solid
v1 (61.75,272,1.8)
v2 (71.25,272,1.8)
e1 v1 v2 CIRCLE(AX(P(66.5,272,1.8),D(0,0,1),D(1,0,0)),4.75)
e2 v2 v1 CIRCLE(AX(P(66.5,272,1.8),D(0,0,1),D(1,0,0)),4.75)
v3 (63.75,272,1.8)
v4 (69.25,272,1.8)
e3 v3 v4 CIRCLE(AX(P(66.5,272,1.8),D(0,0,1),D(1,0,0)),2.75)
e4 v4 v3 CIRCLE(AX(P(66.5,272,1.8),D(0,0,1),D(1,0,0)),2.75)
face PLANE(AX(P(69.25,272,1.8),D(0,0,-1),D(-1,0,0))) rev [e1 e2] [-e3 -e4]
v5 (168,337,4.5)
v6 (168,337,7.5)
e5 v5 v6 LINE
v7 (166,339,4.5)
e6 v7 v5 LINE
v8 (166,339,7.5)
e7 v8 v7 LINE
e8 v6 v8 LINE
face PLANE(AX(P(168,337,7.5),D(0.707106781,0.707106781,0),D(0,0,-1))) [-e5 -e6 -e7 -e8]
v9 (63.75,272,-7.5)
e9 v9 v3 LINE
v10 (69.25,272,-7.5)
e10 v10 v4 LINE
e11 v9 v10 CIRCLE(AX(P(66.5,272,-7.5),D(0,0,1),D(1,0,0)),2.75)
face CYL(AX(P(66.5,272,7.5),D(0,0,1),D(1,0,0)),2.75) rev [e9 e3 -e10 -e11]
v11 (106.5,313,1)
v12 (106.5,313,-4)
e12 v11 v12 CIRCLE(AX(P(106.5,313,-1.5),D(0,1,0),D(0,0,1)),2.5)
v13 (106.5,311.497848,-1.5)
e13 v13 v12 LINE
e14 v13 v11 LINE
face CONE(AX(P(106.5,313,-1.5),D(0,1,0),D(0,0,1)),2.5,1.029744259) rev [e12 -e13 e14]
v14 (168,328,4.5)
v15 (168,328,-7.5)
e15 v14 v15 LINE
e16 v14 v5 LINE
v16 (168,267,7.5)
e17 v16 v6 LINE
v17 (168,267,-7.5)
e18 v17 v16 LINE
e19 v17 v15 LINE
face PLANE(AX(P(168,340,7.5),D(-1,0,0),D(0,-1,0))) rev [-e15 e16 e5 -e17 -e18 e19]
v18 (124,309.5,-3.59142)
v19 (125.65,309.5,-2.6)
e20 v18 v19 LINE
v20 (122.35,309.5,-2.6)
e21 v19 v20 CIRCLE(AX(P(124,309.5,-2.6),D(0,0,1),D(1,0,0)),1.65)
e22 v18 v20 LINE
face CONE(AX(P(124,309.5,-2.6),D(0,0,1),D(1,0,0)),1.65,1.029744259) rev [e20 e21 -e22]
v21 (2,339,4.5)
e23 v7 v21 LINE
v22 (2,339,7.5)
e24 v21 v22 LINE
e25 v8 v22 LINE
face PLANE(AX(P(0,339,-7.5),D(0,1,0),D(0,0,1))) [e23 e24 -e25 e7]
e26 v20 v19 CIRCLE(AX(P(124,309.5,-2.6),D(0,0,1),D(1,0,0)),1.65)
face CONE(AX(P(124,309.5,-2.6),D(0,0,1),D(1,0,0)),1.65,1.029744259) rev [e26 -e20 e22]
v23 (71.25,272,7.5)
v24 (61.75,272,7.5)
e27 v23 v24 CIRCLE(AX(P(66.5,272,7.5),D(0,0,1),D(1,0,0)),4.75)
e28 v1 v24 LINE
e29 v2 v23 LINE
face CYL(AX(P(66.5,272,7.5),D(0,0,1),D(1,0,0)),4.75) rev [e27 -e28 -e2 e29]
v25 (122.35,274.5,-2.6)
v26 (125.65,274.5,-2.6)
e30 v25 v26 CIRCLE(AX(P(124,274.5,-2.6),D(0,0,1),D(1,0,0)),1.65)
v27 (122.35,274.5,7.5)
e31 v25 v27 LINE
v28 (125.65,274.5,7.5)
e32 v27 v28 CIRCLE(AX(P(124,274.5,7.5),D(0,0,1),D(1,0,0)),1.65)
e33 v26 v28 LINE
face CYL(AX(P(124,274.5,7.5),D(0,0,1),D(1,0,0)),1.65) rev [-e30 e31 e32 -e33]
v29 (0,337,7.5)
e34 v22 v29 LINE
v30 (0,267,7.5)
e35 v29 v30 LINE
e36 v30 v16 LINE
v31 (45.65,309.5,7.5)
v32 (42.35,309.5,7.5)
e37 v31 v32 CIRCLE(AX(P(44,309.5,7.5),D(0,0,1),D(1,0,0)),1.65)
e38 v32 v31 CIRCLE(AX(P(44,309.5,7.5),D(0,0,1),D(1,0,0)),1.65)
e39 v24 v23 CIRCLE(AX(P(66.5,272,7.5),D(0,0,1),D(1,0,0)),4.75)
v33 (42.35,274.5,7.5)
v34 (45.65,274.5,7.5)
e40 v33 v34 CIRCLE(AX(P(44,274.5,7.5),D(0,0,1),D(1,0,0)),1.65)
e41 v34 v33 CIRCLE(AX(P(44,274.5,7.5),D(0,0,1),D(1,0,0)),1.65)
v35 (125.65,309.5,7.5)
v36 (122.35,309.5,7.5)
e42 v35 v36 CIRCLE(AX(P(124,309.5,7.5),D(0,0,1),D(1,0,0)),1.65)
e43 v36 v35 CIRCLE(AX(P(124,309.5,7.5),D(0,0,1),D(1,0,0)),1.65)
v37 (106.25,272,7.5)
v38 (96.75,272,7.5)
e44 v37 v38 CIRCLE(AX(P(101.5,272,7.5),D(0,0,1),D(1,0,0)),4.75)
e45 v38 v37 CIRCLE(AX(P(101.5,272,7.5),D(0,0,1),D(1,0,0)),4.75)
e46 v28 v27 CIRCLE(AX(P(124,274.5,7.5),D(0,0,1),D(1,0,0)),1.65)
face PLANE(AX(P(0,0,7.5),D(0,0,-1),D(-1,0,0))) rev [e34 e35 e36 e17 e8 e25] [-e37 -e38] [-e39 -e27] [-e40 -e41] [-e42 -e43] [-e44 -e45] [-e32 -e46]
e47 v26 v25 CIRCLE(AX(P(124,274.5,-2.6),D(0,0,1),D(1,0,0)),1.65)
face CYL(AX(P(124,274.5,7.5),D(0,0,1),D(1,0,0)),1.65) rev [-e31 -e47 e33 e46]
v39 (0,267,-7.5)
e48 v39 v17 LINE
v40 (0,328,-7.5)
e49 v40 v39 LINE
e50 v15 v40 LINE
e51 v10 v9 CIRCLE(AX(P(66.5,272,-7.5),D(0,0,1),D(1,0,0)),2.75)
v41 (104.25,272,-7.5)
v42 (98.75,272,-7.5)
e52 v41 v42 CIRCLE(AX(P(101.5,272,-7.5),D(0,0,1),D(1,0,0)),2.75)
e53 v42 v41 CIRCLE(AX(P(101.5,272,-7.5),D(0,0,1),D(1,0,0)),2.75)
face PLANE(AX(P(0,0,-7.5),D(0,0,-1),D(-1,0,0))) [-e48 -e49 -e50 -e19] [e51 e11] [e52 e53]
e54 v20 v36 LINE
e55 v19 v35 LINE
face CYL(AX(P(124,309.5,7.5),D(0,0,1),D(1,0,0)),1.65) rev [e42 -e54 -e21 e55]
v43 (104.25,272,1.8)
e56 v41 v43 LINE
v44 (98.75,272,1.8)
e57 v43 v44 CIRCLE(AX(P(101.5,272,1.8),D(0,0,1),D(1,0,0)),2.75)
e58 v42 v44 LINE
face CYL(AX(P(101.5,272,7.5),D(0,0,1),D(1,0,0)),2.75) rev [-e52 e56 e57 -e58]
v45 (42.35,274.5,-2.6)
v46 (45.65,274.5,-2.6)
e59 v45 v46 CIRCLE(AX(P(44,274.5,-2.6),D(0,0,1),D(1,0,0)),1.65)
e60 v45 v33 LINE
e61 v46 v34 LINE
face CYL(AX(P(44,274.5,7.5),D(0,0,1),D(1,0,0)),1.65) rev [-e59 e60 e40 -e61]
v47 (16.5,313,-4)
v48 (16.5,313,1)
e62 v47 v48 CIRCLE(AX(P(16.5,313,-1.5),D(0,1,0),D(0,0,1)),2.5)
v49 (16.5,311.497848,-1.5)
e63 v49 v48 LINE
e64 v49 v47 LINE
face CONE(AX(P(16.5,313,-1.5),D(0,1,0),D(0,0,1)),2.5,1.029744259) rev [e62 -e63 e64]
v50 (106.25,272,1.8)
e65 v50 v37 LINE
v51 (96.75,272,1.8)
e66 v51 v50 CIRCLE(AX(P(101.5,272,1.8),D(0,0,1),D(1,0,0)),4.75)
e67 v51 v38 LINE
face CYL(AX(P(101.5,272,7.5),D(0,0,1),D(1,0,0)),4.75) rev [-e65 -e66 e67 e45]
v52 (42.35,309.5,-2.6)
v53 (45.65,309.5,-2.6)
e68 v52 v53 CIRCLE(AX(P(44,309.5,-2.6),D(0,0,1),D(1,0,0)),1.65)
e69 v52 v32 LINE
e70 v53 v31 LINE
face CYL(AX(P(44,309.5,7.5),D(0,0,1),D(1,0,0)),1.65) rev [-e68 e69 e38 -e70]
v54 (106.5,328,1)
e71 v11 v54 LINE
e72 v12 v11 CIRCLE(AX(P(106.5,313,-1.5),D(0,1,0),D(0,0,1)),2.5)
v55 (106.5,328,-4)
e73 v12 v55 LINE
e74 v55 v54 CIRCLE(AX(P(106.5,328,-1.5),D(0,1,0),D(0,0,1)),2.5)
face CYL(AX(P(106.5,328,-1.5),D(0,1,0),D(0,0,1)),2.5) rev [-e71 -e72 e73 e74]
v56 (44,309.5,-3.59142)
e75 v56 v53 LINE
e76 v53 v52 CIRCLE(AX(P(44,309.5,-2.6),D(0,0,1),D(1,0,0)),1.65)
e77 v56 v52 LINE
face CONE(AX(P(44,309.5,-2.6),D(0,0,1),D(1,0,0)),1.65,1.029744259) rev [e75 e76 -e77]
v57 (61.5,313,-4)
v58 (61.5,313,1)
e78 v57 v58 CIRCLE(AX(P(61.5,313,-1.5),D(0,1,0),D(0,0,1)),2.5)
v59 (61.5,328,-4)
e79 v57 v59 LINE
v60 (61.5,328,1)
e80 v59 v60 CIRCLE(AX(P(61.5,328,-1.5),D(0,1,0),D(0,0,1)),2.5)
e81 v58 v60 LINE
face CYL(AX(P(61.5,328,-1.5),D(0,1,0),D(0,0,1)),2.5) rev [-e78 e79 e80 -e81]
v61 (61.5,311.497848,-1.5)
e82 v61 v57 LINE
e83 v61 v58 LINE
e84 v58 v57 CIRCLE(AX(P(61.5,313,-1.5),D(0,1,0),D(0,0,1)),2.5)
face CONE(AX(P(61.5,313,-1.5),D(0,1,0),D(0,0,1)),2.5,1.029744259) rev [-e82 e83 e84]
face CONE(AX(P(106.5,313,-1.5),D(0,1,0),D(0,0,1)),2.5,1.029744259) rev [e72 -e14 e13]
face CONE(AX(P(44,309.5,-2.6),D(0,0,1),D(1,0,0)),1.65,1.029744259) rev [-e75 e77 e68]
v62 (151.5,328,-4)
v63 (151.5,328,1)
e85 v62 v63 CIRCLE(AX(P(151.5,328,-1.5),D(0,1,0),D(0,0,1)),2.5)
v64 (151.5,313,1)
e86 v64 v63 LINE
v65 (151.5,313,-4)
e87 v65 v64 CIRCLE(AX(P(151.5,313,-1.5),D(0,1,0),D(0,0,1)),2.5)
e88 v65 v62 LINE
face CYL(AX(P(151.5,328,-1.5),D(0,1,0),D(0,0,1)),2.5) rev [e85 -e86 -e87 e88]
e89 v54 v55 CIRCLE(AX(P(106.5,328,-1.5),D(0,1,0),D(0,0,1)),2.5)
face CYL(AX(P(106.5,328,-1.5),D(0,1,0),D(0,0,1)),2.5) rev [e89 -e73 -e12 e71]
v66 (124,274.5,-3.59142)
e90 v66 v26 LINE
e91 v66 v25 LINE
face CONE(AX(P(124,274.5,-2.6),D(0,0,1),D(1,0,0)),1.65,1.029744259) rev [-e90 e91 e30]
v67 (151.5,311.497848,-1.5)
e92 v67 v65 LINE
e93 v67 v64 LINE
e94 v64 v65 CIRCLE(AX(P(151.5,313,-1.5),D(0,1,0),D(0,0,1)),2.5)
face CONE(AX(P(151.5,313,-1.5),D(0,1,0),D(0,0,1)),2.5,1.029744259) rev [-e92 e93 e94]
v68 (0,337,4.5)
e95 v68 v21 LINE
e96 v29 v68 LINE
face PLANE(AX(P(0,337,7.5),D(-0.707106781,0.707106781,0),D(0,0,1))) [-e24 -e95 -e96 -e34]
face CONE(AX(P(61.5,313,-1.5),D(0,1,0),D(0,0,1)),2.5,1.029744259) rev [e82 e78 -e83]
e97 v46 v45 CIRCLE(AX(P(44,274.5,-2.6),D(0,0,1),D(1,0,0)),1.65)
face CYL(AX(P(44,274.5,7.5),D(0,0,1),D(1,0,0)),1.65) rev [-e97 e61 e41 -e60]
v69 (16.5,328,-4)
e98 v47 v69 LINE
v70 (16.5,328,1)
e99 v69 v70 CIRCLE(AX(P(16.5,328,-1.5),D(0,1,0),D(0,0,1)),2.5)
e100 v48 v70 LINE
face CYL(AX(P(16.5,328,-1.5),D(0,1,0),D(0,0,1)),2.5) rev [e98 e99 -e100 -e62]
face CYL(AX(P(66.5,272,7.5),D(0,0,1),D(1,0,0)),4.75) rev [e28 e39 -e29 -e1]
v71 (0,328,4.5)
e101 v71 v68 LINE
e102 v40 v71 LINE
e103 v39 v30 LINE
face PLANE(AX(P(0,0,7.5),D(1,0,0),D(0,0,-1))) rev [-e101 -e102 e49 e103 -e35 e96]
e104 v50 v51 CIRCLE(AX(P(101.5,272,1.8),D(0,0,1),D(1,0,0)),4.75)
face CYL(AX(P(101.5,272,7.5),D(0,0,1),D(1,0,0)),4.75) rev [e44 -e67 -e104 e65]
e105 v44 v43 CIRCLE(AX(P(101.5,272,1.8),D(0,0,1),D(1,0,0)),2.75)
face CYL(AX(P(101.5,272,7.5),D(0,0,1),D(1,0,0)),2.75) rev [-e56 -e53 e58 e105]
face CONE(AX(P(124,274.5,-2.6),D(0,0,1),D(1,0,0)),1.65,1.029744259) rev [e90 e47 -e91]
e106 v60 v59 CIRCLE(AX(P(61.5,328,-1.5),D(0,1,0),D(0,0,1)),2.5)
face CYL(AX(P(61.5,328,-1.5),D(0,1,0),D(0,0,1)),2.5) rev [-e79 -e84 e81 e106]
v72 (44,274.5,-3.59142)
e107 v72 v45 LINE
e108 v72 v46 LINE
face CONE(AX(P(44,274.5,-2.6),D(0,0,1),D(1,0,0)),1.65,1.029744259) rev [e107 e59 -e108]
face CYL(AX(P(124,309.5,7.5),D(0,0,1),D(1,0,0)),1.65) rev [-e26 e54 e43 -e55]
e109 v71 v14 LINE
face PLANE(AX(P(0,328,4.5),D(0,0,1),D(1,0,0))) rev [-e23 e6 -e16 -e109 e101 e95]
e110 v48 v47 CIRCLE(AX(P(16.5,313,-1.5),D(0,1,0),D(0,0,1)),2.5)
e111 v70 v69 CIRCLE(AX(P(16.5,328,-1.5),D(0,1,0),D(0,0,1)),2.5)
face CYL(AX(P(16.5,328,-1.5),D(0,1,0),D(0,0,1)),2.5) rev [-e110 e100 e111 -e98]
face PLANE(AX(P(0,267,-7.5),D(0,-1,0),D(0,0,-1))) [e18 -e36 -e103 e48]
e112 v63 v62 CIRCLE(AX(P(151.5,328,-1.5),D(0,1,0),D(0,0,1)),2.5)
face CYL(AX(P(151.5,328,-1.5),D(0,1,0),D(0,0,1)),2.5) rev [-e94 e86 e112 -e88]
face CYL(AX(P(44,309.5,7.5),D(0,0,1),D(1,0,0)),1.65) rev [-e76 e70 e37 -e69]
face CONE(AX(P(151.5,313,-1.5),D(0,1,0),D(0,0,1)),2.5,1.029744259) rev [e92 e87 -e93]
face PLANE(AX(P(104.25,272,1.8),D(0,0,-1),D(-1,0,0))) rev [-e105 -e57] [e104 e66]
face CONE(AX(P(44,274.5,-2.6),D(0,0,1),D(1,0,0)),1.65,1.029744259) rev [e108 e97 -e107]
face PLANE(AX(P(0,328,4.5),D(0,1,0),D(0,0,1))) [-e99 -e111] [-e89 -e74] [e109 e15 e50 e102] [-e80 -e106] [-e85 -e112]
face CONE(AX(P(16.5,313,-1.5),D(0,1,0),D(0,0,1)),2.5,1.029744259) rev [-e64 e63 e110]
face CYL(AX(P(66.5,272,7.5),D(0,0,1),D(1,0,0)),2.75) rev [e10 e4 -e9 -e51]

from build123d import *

# Parameters (mm, degrees)
BOSS_EXTRUDE1_DEPTH                                  = 7.5
SKETCH2_W                                            = 168
SKETCH2_H                                            = 12
CUT_EXTRUDE1_DEPTH                                   = 12
CUT_EXTRUDE2_DEPTH                                   = 489.185415595
SKETCH4_W                                            = 22
SKETCH4_H                                            = 220
CUT_EXTRUDE3_DEPTH                                   = 1.5
F_11_0_11_DIAMETER_HOLE1_D                           = 11
F_11_0_11_DIAMETER_HOLE1_DEPTH                       = 30
SKETCH17_W                                           = 13.5
SKETCH17_H                                           = 16
CUT_EXTRUDE4_DEPTH                                   = 5
M6_TAPPED_HOLE2_D                                    = 5
M6_TAPPED_HOLE2_DEPTH                                = 15
M6_TAPPED_HOLE2_TIP                                  = 1.502151548
M4_TAPPED_HOLE1_D                                    = 3.3
M4_TAPPED_HOLE1_DEPTH                                = 10.1
M4_TAPPED_HOLE1_TIP                                  = 0.991420021
HOLE_SIZE_PER_SOCKET_HEAD_CAP_SCREW_TYPE_D           = 11
HOLE_SIZE_PER_SOCKET_HEAD_CAP_SCREW_TYPE_CBORE_D     = 18
HOLE_SIZE_PER_SOCKET_HEAD_CAP_SCREW_TYPE_CBORE_DEPTH = 11
F_10_0_10_DIAMETER_HOLE1_D                           = 10
F_10_0_10_DIAMETER_HOLE1_DEPTH                       = 30
F_10_0_10_DIAMETER_HOLE1_TIP                         = 3.004303095
M8_TAPPED_HOLE3_D                                    = 6.8
M8_TAPPED_HOLE3_DEPTH                                = 19.75
M8_TAPPED_HOLE3_TIP                                  = 2.042926105
M6_TAPPED_HOLE3_D                                    = 5
M6_TAPPED_HOLE3_DEPTH                                = 15
M6_TAPPED_HOLE3_TIP                                  = 1.502151548
FILLET1_R                                            = 5
M5_TAPPED_HOLE1_D                                    = 4.2
M5_TAPPED_HOLE1_DEPTH                                = 12.4
M5_TAPPED_HOLE1_TIP                                  = 1.2618073
CHAMFER1_SIZE                                        = 1
SKETCH36_OUTSIDE_W                                   = 449.638
SKETCH36_OUTSIDE_H                                   = 439.638
SKETCH36_OUTSIDE_W_2                                 = 200
SKETCH36_OUTSIDE_H_2                                 = 72
CUT_EXTRUDE6_DEPTH                                   = 489.185415598
M4_TAPPED_HOLE2_D                                    = 3.3
M4_TAPPED_HOLE2_DEPTH                                = 10.1
M4_TAPPED_HOLE2_TIP                                  = 0.991420021
HOLE_SIZE_PER_SOCKET_HEAD_CAP_SCREW_2_D              = 5.5
HOLE_SIZE_PER_SOCKET_HEAD_CAP_SCREW_2_CBORE_D        = 9.5
HOLE_SIZE_PER_SOCKET_HEAD_CAP_SCREW_2_CBORE_DEPTH    = 5.7
CHAMFER2_SIZE                                        = 2


with BuildPart() as part:
    # Sketch1 → Boss-Extrude1 (new, symmetric)
    with BuildSketch(Plane.XY):
        Polygon((0, 0), (0, 340), (168, 340), (168, 220), (350, 220), (350, 0), align=None)
    extrude(amount=BOSS_EXTRUDE1_DEPTH, both=True)

    # Sketch2 → Cut-Extrude1 (cut)
    with BuildSketch(Plane(origin=(0, 340, 0), x_dir=(1, 0, 0), z_dir=(0, 1, 0))):
        with Locations((84, 1.5)):
            Rectangle(SKETCH2_W, SKETCH2_H)
    extrude(amount=-CUT_EXTRUDE1_DEPTH, mode=Mode.SUBTRACT)

    # Sketch3 → Cut-Extrude2 (cut, through all)
    with BuildSketch(Plane.XY.offset(7.5)):
        with BuildLine():
            Line((45, 110), (135, 110))
            ThreePointArc((135, 110), (138.535533906, 108.535533906), (140, 105))
            Line((140, 105), (140, 35))
            ThreePointArc((140, 35), (138.535533906, 31.464466094), (135, 30))
            Line((135, 30), (45, 30))
            ThreePointArc((45, 30), (41.464466094, 31.464466094), (40, 35))
            Line((40, 35), (40, 105))
            ThreePointArc((40, 105), (41.464466094, 108.535533906), (45, 110))
        make_face()
        with BuildLine():
            Line((215, 30), (305, 30))
            ThreePointArc((305, 30), (308.535533906, 31.464466094), (310, 35))
            Line((310, 35), (310, 105))
            ThreePointArc((310, 105), (308.535533906, 108.535533906), (305, 110))
            Line((305, 110), (215, 110))
            ThreePointArc((215, 110), (211.464466094, 108.535533906), (210, 105))
            Line((210, 105), (210, 35))
            ThreePointArc((210, 35), (211.464466094, 31.464466094), (215, 30))
        make_face()
    extrude(amount=-CUT_EXTRUDE2_DEPTH, mode=Mode.SUBTRACT)

    # Sketch4 → Cut-Extrude3 (cut)
    with BuildSketch(Plane(origin=(0, 0, -7.5), x_dir=(-1, 0, 0), z_dir=(0, 0, -1))):
        with Locations((-339, 110)):
            Rectangle(SKETCH4_W, SKETCH4_H)
    extrude(amount=-CUT_EXTRUDE3_DEPTH, mode=Mode.SUBTRACT)

    # Ø11.0 (11) Diameter Hole1
    with Locations(Plane(origin=(0, 30, 0), x_dir=(-1, 0, 0), z_dir=(0, 1, 0))):
        with Locations((-285, 0), (-65, 0), (-235, 0), (-115, 0)):
            Hole(F_11_0_11_DIAMETER_HOLE1_D / 2, depth=F_11_0_11_DIAMETER_HOLE1_DEPTH)

    # Sketch17 → Cut-Extrude4 (cut)
    with BuildSketch(Plane(origin=(350, 0, 0), x_dir=(0, 0, -1), z_dir=(1, 0, 0))):
        with Locations((-0.75, 160)):
            Rectangle(SKETCH17_W, SKETCH17_H)
    extrude(amount=-CUT_EXTRUDE4_DEPTH, mode=Mode.SUBTRACT)

    # M6 Tapped Hole2
    with Locations(Plane(origin=(0, 0, -7.5), x_dir=(-1, 0, 0), z_dir=(0, 0, -1))):
        with Locations((-290.5, 15), (-256.5, 15)):
            Hole(M6_TAPPED_HOLE2_D / 2, depth=M6_TAPPED_HOLE2_DEPTH)
            with Locations((0, 0, -(M6_TAPPED_HOLE2_DEPTH + M6_TAPPED_HOLE2_TIP / 2))):  # 118° drill point
                Cone(0, M6_TAPPED_HOLE2_D / 2, M6_TAPPED_HOLE2_TIP, mode=Mode.SUBTRACT)

    # M4 Tapped Hole1
    with Locations(Plane(origin=(0, 0, -6), x_dir=(-1, 0, 0), z_dir=(0, 0, -1))):
        with Locations((-335.5, 200), (-335.5, 140), (-335.5, 80), (-335.5, 20)):
            Hole(M4_TAPPED_HOLE1_D / 2, depth=M4_TAPPED_HOLE1_DEPTH)
            with Locations((0, 0, -(M4_TAPPED_HOLE1_DEPTH + M4_TAPPED_HOLE1_TIP / 2))):  # 118° drill point
                Cone(0, M4_TAPPED_HOLE1_D / 2, M4_TAPPED_HOLE1_TIP, mode=Mode.SUBTRACT)

    # Hole size per socket head cap screw type (through all)
    with Locations(Plane.XY.offset(7.5)):
        with Locations((70, 202), (100, 202), (130, 202), (130, 162), (100, 162), (70, 162)):
            CounterBoreHole(HOLE_SIZE_PER_SOCKET_HEAD_CAP_SCREW_TYPE_D / 2, HOLE_SIZE_PER_SOCKET_HEAD_CAP_SCREW_TYPE_CBORE_D / 2, HOLE_SIZE_PER_SOCKET_HEAD_CAP_SCREW_TYPE_CBORE_DEPTH)

    # Ø10.0 (10) Diameter Hole1
    with Locations(Plane.XY.offset(7.5)):
        with Locations((135, 135), (65, 135)):
            Hole(F_10_0_10_DIAMETER_HOLE1_D / 2, depth=F_10_0_10_DIAMETER_HOLE1_DEPTH)
            with Locations((0, 0, -(F_10_0_10_DIAMETER_HOLE1_DEPTH + F_10_0_10_DIAMETER_HOLE1_TIP / 2))):  # 118° drill point
                Cone(0, F_10_0_10_DIAMETER_HOLE1_D / 2, F_10_0_10_DIAMETER_HOLE1_TIP, mode=Mode.SUBTRACT)

    # M8 Tapped Hole3
    with Locations(Plane(origin=(350, 0, 0), x_dir=(0, 0, -1), z_dir=(1, 0, 0))):
        with Locations((0, 187.5), (0, 132.5)):
            Hole(M8_TAPPED_HOLE3_D / 2, depth=M8_TAPPED_HOLE3_DEPTH)
            with Locations((0, 0, -(M8_TAPPED_HOLE3_DEPTH + M8_TAPPED_HOLE3_TIP / 2))):  # 118° drill point
                Cone(0, M8_TAPPED_HOLE3_D / 2, M8_TAPPED_HOLE3_TIP, mode=Mode.SUBTRACT)

    # M6 Tapped Hole3
    with Locations(Plane(origin=(0, 328, 0), x_dir=(-1, 0, 0), z_dir=(0, 1, 0))):
        with Locations((-151.5, -1.5), (-106.5, -1.5), (-61.5, -1.5), (-16.5, -1.5)):
            Hole(M6_TAPPED_HOLE3_D / 2, depth=M6_TAPPED_HOLE3_DEPTH)
            with Locations((0, 0, -(M6_TAPPED_HOLE3_DEPTH + M6_TAPPED_HOLE3_TIP / 2))):  # 118° drill point
                Cone(0, M6_TAPPED_HOLE3_D / 2, M6_TAPPED_HOLE3_TIP, mode=Mode.SUBTRACT)

    # Fillet1
    fillet1_edges = [part.edges().sort_by_distance(p)[0] for p in [
        (168, 220, 0),
    ]]
    fillet(fillet1_edges, radius=FILLET1_R)

    # M5 Tapped Hole1
    with Locations(Plane(origin=(345, 0, 0), x_dir=(0, 0, -1), z_dir=(1, 0, 0))):
        with Locations((4, 160)):
            Hole(M5_TAPPED_HOLE1_D / 2, depth=M5_TAPPED_HOLE1_DEPTH)
            with Locations((0, 0, -(M5_TAPPED_HOLE1_DEPTH + M5_TAPPED_HOLE1_TIP / 2))):  # 118° drill point
                Cone(0, M5_TAPPED_HOLE1_D / 2, M5_TAPPED_HOLE1_TIP, mode=Mode.SUBTRACT)

    # Chamfer1
    chamfer1_edges = [part.edges().sort_by_distance(p)[0] for p in [
        (0, 0, 0),
        (0, 340, 6),
        (168, 340, 6),
        (350, 220, 0.75),
        (350, 0, 0.75),
    ]]
    chamfer(chamfer1_edges, length=CHAMFER1_SIZE)

    # Sketch36 outside → Cut-Extrude6 (cut, through all)
    with BuildSketch(Plane.XY.offset(7.5)):
        with Locations((175, 170)):
            Rectangle(SKETCH36_OUTSIDE_W, SKETCH36_OUTSIDE_H)
        with Locations((100, 303)):
            Rectangle(SKETCH36_OUTSIDE_W_2, SKETCH36_OUTSIDE_H_2, mode=Mode.SUBTRACT)
    extrude(amount=-CUT_EXTRUDE6_DEPTH, mode=Mode.SUBTRACT)

    # M4 Tapped Hole2
    with Locations(Plane.XY.offset(7.5)):
        with Locations((44, 309.5), (44, 274.5), (124, 274.5), (124, 309.5)):
            Hole(M4_TAPPED_HOLE2_D / 2, depth=M4_TAPPED_HOLE2_DEPTH)
            with Locations((0, 0, -(M4_TAPPED_HOLE2_DEPTH + M4_TAPPED_HOLE2_TIP / 2))):  # 118° drill point
                Cone(0, M4_TAPPED_HOLE2_D / 2, M4_TAPPED_HOLE2_TIP, mode=Mode.SUBTRACT)

    # Hole size per socket head cap screw  2 (through all)
    with Locations(Plane.XY.offset(7.5)):
        with Locations((66.5, 272), (101.5, 272)):
            CounterBoreHole(HOLE_SIZE_PER_SOCKET_HEAD_CAP_SCREW_2_D / 2, HOLE_SIZE_PER_SOCKET_HEAD_CAP_SCREW_2_CBORE_D / 2, HOLE_SIZE_PER_SOCKET_HEAD_CAP_SCREW_2_CBORE_DEPTH)

    # Chamfer2
    chamfer2_edges = [part.edges().sort_by_distance(p)[0] for p in [
        (168, 339, 6),
        (0, 339, 6),
    ]]
    chamfer(chamfer2_edges, length=CHAMFER2_SIZE)


solid = part.part
